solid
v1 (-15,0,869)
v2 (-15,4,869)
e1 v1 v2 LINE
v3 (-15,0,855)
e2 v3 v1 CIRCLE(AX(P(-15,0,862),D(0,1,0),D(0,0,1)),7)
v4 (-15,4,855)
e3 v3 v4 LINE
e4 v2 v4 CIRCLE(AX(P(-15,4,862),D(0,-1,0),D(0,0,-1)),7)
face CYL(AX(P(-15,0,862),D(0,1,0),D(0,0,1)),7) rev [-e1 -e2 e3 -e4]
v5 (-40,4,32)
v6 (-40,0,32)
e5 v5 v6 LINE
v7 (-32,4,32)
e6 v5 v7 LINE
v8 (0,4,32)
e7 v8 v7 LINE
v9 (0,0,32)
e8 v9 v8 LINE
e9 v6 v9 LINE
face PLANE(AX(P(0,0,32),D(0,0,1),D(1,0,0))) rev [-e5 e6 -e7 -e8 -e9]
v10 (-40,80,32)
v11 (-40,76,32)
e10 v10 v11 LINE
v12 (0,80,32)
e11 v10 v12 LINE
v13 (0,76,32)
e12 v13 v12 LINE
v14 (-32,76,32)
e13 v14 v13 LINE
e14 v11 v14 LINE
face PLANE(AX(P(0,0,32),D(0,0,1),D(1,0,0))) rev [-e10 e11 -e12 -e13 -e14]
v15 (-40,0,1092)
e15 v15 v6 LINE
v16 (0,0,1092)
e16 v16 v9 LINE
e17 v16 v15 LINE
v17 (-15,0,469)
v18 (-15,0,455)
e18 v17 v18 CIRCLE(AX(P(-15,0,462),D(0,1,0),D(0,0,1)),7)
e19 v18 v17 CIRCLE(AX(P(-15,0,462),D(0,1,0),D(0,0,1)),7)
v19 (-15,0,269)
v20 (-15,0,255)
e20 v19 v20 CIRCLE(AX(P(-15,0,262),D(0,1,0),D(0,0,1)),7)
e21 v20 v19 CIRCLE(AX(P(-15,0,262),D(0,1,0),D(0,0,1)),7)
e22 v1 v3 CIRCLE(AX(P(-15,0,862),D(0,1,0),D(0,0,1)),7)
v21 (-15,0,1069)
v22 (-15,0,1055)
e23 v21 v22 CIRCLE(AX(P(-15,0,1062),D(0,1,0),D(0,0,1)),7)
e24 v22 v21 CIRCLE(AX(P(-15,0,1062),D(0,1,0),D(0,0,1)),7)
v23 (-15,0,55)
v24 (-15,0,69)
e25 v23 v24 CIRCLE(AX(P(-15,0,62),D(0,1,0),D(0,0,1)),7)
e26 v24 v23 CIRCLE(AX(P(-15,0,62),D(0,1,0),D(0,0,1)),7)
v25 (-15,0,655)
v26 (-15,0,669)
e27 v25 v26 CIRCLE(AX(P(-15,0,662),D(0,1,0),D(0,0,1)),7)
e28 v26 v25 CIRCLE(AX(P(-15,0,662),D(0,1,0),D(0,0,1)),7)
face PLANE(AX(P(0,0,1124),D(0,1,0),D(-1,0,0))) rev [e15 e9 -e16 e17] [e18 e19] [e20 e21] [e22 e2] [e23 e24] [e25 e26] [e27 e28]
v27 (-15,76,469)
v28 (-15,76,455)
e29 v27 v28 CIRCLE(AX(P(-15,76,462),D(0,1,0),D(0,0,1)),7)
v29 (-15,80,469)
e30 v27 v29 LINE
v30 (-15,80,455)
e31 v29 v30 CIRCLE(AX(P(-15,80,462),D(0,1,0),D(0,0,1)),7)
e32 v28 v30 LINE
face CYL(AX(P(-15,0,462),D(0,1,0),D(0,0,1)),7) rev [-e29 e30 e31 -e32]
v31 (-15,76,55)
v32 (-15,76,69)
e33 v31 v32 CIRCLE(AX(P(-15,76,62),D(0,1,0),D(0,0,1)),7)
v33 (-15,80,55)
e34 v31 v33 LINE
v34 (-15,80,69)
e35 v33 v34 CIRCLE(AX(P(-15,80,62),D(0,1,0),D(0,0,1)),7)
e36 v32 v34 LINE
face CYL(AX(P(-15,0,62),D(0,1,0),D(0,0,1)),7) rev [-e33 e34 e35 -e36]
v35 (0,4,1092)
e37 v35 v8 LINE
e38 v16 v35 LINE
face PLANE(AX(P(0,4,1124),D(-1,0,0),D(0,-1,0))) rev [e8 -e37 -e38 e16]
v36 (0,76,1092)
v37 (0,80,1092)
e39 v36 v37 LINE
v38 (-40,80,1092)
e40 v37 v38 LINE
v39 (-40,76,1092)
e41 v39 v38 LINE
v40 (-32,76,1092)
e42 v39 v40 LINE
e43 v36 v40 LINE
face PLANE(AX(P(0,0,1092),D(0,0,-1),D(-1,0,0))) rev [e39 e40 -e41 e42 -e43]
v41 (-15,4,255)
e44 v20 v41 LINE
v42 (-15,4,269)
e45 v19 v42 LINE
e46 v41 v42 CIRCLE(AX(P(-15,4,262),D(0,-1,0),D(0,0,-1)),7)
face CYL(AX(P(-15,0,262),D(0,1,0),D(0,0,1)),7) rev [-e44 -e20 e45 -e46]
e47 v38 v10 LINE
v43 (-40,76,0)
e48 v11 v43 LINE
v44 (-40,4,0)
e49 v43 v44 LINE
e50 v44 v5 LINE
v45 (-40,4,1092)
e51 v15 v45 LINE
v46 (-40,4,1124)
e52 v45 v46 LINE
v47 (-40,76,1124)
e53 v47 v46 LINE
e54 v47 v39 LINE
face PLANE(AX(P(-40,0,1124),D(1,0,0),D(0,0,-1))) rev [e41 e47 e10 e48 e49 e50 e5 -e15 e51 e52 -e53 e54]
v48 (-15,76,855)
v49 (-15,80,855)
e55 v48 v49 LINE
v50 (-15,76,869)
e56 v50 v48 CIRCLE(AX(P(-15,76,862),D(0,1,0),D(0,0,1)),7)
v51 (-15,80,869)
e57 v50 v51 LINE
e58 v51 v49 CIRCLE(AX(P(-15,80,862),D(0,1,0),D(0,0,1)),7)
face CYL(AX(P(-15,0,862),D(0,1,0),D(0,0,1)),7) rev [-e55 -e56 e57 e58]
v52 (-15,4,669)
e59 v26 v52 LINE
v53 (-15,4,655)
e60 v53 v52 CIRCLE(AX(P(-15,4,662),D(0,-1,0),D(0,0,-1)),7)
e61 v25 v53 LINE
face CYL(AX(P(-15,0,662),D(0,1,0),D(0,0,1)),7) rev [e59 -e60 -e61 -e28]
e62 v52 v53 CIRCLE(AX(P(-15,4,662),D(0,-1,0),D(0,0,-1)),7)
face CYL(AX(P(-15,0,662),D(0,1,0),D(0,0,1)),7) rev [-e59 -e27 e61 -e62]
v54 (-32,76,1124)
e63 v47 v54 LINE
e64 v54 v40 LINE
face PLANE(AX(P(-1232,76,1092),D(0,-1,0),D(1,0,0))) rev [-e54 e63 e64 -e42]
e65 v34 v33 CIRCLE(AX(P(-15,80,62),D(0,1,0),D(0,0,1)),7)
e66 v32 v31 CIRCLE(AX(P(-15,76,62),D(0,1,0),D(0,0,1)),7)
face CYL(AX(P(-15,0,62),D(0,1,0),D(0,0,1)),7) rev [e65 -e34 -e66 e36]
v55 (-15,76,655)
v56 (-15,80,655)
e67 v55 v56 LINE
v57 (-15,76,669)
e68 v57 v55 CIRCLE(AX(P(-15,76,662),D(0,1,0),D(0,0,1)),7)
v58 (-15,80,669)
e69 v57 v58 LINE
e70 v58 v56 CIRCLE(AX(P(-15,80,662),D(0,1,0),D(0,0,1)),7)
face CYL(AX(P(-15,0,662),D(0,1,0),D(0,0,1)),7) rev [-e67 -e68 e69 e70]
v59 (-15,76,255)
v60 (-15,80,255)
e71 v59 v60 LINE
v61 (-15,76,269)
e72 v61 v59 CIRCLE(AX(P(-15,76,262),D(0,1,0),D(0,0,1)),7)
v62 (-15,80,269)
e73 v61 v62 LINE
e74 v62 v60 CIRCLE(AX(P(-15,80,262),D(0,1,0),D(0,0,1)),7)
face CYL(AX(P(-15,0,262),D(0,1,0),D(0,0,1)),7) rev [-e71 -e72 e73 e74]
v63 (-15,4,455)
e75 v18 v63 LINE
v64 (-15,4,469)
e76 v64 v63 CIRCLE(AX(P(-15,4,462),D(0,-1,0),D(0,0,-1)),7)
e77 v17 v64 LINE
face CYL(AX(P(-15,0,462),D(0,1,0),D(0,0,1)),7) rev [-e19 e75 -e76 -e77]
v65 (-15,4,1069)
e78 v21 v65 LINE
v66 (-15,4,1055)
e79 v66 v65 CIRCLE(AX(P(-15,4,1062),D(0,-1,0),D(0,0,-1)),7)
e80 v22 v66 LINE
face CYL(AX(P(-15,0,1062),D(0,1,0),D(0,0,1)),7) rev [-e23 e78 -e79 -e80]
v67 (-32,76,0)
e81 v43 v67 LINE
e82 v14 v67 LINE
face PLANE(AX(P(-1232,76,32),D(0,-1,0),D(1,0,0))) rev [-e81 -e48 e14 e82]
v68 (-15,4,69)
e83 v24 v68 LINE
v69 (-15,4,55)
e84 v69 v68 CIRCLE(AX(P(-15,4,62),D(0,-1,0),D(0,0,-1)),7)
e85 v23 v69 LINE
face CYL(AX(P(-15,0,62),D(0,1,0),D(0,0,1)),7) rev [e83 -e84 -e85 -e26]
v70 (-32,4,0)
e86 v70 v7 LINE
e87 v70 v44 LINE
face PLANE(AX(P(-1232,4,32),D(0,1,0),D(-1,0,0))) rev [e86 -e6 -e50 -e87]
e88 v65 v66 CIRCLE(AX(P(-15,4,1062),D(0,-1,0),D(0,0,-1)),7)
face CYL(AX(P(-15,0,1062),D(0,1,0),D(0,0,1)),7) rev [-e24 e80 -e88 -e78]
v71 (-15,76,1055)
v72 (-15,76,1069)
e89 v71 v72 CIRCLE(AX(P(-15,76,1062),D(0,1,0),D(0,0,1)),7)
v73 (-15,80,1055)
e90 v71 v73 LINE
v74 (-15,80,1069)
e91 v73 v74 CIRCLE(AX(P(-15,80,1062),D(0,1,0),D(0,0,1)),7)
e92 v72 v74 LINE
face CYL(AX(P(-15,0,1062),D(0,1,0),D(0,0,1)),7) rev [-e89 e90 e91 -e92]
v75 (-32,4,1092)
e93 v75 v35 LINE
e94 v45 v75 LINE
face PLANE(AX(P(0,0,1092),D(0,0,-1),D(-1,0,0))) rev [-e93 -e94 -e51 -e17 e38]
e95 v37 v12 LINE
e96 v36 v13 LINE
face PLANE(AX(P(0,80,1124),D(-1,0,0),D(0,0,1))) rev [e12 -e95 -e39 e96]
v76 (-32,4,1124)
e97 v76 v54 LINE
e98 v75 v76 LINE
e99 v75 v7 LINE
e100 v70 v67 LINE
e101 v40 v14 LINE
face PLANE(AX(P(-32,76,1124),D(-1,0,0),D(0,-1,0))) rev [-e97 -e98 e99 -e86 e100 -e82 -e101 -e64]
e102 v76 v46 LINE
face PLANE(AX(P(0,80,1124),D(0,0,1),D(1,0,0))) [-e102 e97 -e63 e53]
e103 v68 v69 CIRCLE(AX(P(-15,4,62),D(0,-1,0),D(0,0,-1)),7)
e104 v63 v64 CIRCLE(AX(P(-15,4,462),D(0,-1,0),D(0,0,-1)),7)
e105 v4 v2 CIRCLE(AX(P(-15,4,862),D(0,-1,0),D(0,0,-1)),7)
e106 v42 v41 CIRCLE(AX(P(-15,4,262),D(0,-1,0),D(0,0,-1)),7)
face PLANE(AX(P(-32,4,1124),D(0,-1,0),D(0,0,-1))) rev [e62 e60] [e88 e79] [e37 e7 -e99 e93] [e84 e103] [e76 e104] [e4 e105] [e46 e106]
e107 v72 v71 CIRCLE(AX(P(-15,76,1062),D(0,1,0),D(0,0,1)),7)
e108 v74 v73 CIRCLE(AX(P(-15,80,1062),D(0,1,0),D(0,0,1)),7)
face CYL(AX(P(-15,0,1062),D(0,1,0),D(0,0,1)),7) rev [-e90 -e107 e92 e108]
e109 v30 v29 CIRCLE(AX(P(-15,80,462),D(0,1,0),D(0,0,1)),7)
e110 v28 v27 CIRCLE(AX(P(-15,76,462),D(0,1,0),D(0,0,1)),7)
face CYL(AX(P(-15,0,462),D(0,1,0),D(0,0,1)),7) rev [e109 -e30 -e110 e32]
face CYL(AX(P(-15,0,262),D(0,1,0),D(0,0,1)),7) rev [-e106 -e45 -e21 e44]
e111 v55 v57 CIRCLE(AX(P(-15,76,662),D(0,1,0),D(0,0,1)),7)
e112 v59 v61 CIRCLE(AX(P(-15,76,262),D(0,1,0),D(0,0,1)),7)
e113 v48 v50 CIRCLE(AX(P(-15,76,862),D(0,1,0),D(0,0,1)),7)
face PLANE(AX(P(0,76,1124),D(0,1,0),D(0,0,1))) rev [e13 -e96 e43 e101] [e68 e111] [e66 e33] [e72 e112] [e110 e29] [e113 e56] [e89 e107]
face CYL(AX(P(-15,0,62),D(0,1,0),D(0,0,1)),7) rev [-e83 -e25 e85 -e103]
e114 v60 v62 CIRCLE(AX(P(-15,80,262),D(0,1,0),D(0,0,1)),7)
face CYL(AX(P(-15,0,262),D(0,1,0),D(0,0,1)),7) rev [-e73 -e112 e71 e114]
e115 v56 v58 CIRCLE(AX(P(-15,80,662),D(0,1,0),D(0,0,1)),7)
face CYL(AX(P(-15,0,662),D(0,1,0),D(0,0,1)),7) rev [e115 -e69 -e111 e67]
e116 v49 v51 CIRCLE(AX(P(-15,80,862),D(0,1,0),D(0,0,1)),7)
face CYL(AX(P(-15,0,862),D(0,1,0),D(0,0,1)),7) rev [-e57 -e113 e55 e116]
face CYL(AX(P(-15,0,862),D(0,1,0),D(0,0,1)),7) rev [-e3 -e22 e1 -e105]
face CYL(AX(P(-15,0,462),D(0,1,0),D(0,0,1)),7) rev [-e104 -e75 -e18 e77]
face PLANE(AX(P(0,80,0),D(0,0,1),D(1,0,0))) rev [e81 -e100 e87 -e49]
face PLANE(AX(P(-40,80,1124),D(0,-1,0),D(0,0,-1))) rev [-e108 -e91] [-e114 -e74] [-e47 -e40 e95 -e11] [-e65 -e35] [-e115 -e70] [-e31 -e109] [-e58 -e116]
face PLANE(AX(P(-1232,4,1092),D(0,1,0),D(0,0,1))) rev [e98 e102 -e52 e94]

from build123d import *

# Parameters (mm, degrees)
EXTRUDE1_DEPTH     = 1124
SKETCH2_W          = 32
SKETCH2_H          = 32
CUT_EXTRUDE1_DEPTH = 1128.553102962
SKETCH3_W          = 32
SKETCH3_H          = 4
CUT_EXTRUDE2_DEPTH = 1200
SKETCH4_R          = 7
CUT_EXTRUDE3_DEPTH = 1128.553102962
LPATTERN1_COUNT    = 6
LPATTERN1_PITCH    = 200


with BuildPart() as part:
    # Sketch1 → Extrude1 (new body)
    with BuildSketch(Plane.XY):
        Polygon((0, 0), (-40, 0), (-40, 80), (0, 80), (0, 76), (-32, 76), (-32, 4), (0, 4), align=None)
    extrude(amount=EXTRUDE1_DEPTH)

    # Sketch2 → Cut-Extrude1 (cut, through all)
    with BuildSketch(Plane(origin=(0, 80, 0), x_dir=(1, 0, 0), z_dir=(0, 1, 0))):
        with Locations((-16, -16)):
            Rectangle(SKETCH2_W, SKETCH2_H)
        with Locations((-16, -1108)):
            Rectangle(SKETCH2_W, SKETCH2_H)
    extrude(amount=-CUT_EXTRUDE1_DEPTH, mode=Mode.SUBTRACT)

    # Sketch3 → Cut-Extrude2 (cut)
    with BuildSketch(Plane(origin=(-32, 0, 0), x_dir=(0, 0, -1), z_dir=(1, 0, 0))):
        with Locations((-1108, 78)):
            Rectangle(SKETCH3_W, SKETCH3_H)
        with Locations((-1108, 2)):
            Rectangle(SKETCH3_W, SKETCH3_H)
        with Locations((-16, 78)):
            Rectangle(SKETCH3_W, SKETCH3_H)
        with Locations((-16, 2)):
            Rectangle(SKETCH3_W, SKETCH3_H)
    extrude(amount=-CUT_EXTRUDE2_DEPTH, mode=Mode.SUBTRACT)

    # Sketch4 → Cut-Extrude3 (cut, through all)
    with BuildSketch(Plane(origin=(0, 80, 0), x_dir=(1, 0, 0), z_dir=(0, 1, 0))):
        with Locations(Location((-15, -1062, 0), (0, 0, 270))):
            Circle(SKETCH4_R)
    cut_extrude3 = extrude(amount=-CUT_EXTRUDE3_DEPTH, mode=Mode.SUBTRACT)

    # LPattern1: Cut-Extrude3 ×6
    with Locations(*[(0, 0, -i * LPATTERN1_PITCH) for i in range(1, LPATTERN1_COUNT)]):
        add(cut_extrude3, mode=Mode.SUBTRACT)


solid = part.part
